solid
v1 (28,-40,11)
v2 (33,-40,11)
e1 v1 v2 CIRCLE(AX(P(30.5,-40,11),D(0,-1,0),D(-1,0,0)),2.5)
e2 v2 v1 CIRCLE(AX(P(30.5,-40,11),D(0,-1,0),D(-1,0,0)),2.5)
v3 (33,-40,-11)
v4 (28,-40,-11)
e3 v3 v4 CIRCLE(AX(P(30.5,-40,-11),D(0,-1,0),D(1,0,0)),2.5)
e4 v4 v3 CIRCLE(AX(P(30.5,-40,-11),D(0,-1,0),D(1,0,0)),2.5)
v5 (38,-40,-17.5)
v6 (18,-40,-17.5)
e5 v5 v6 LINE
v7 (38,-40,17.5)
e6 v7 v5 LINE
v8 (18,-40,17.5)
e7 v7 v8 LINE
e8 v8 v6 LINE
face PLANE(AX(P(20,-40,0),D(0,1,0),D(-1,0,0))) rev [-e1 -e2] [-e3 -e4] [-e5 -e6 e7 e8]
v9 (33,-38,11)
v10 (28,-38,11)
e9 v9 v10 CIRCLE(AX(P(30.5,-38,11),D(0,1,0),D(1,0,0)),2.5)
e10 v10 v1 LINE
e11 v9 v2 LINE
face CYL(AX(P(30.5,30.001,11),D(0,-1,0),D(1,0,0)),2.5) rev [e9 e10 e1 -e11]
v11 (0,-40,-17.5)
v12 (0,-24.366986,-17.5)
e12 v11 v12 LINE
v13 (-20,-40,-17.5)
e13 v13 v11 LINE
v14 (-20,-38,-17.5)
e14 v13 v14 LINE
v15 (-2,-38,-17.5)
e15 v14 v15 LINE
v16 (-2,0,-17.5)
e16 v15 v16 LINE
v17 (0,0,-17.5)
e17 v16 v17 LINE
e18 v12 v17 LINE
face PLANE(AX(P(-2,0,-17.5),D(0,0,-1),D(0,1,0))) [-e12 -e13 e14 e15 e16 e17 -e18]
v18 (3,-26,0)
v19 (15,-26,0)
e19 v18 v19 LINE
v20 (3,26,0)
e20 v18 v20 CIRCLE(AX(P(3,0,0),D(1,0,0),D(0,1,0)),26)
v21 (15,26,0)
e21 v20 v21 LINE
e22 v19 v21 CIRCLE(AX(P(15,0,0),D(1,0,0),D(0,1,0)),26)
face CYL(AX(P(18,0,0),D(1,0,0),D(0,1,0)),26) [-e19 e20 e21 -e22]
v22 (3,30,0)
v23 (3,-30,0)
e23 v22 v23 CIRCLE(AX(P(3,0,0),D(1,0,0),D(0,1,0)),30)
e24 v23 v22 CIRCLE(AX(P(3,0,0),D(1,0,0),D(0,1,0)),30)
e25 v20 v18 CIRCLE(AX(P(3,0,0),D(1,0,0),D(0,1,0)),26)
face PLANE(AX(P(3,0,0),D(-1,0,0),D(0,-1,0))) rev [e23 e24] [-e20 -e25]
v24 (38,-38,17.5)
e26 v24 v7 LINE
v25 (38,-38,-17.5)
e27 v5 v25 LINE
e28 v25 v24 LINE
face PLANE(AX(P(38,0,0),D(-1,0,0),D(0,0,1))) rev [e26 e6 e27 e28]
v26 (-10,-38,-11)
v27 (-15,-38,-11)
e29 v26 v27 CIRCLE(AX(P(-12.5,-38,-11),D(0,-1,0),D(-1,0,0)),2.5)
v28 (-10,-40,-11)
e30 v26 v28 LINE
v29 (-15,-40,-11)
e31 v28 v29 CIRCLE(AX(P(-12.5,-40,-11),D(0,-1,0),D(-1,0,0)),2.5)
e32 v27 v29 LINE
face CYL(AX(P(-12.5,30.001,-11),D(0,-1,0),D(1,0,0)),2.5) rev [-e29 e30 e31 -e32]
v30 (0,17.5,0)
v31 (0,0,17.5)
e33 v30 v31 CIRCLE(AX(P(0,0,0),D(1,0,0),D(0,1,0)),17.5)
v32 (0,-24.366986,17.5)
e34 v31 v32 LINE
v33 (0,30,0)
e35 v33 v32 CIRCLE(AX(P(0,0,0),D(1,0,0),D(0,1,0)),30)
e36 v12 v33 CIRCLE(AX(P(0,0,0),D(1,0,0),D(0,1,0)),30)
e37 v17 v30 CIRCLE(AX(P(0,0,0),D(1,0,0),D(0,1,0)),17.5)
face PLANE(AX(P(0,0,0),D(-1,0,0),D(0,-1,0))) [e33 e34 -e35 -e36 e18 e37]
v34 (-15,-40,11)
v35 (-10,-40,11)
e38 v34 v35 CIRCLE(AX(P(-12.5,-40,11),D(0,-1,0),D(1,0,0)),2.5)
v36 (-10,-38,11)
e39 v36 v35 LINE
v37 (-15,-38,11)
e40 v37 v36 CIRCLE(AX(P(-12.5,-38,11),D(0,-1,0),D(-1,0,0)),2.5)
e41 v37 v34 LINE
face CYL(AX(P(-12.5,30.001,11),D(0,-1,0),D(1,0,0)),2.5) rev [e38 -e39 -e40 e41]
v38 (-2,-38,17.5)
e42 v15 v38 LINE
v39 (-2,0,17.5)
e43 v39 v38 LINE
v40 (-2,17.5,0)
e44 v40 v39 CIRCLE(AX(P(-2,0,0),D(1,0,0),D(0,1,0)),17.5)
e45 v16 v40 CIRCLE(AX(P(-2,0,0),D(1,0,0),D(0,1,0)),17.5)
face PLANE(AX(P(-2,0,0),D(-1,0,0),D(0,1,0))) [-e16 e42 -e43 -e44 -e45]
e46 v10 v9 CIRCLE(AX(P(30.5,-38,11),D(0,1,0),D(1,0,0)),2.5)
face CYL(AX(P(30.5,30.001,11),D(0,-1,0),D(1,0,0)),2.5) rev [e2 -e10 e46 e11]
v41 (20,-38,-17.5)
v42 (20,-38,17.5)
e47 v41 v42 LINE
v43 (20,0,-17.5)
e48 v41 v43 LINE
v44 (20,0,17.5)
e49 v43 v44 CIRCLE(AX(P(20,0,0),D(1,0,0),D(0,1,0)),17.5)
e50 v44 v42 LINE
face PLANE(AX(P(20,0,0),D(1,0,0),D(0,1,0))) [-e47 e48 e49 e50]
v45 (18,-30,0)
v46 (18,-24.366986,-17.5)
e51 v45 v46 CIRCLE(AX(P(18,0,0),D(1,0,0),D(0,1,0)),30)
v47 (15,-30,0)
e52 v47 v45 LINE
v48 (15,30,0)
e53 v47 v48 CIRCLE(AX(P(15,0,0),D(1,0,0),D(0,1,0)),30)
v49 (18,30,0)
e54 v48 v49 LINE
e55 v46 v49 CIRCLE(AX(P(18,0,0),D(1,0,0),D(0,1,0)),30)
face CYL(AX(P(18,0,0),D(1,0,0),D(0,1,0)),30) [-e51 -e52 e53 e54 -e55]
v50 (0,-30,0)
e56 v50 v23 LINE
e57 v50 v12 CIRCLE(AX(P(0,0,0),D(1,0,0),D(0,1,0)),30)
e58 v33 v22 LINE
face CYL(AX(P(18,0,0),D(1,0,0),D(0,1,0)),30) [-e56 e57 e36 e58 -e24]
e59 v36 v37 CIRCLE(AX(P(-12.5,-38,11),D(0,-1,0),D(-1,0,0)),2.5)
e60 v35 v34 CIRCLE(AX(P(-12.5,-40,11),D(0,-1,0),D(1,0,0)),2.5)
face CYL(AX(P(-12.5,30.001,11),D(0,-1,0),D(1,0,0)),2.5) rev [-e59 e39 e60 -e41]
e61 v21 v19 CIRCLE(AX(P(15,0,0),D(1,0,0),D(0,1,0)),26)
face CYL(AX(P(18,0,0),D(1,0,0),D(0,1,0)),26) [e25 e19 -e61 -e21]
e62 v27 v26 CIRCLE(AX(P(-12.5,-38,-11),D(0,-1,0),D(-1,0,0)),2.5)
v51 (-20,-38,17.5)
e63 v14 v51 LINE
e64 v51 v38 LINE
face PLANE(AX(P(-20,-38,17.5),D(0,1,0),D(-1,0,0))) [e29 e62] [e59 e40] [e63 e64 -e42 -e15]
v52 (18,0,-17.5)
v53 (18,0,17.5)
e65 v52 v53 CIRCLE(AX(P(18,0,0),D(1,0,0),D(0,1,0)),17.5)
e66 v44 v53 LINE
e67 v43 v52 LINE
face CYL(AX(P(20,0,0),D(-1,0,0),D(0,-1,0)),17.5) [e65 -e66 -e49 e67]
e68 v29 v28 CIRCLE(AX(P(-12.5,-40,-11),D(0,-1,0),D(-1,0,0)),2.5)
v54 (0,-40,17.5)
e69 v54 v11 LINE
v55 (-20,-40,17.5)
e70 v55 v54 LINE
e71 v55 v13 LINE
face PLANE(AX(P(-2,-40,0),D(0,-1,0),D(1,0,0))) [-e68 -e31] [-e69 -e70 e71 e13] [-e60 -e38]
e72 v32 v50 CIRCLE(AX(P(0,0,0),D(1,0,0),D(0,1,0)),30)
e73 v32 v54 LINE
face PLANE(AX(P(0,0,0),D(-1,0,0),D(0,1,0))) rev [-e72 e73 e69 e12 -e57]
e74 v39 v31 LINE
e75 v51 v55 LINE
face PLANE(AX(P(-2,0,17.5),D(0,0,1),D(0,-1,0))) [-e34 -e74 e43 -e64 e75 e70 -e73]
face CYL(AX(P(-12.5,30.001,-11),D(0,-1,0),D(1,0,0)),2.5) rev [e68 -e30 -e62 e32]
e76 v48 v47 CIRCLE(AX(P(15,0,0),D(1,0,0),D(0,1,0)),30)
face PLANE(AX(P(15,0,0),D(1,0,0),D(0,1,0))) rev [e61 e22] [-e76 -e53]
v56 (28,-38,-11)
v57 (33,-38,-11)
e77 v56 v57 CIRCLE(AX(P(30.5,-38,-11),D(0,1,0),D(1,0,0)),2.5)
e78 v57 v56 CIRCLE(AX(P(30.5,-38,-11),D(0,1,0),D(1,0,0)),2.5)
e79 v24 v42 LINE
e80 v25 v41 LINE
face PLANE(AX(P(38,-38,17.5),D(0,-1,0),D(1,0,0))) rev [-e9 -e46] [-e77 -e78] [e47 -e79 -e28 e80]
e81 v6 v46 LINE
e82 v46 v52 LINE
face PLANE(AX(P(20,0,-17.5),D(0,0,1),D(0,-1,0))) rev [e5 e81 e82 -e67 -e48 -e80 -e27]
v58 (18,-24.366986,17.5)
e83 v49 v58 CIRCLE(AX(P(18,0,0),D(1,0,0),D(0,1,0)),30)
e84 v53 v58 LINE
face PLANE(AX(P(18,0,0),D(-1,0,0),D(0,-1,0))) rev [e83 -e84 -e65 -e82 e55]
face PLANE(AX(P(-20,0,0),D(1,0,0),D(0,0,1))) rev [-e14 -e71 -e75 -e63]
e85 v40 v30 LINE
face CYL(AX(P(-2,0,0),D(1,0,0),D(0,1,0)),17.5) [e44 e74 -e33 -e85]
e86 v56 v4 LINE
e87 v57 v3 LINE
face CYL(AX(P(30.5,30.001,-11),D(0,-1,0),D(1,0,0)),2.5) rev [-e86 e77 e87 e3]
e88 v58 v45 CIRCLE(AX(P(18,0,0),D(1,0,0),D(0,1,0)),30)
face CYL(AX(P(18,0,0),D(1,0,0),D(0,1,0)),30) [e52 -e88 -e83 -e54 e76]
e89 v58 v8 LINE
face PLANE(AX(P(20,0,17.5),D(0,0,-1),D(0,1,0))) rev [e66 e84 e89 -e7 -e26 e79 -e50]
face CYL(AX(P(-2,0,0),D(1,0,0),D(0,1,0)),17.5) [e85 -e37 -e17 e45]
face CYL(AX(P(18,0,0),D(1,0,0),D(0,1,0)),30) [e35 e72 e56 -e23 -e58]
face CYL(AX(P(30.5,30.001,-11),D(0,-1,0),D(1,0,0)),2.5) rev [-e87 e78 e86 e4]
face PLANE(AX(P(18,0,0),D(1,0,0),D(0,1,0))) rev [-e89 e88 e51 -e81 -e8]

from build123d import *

# Parameters (mm, degrees)
EXTRUDE_1_DEPTH     = 2
SKETCH_3_W          = 35
SKETCH_3_H          = 2
EXTRUDE_2_DEPTH     = 18
CUT_EXTRUDE_1_REACH = 87.112
SKETCH_4_R          = 2.5


with BuildPart() as part:
    # 草图1 → 旋转1 (revolve)
    with BuildSketch(Plane.XY):
        Polygon((0, 30), (0, 18.550632587), (0, 0), (18, 0), (18, 30), (15, 30), (15, 26), (3, 26), (3, 30), align=None)
    revolve(axis=Axis((18, 0, 0), (-1, 0, 0)))

    # 草图2 → 凸台-拉伸1 (add)
    with BuildSketch(Plane(origin=(18, 0, 0), x_dir=(0, 0, -1), z_dir=(1, 0, 0))):
        with BuildLine():
            Line((17.5, -40), (17.5, 0))
            ThreePointArc((17.5, 0), (0, 17.5), (-17.5, 0))
            Line((-17.5, 0), (-17.5, -40))
            Line((-17.5, -40), (17.5, -40))
        make_face()
    extrude_1 = extrude(amount=EXTRUDE_1_DEPTH)

    # 草图3 → 凸台-拉伸2 (add)
    with BuildSketch(Plane(origin=(20, 0, 0), x_dir=(0, 0, -1), z_dir=(1, 0, 0))):
        with Locations((0, -39)):
            Rectangle(SKETCH_3_W, SKETCH_3_H)
    extrude_2 = extrude(amount=EXTRUDE_2_DEPTH)

    # 镜向1: 凸台-拉伸1, 凸台-拉伸2 across plane
    add(extrude_1.mirror(Plane(origin=(9, 0, 0), x_dir=(0, 0, 1), z_dir=(1, 0, 0))))
    add(extrude_2.mirror(Plane(origin=(9, 0, 0), x_dir=(0, 0, 1), z_dir=(1, 0, 0))))

    # 草图4 → 切除-拉伸1 (cut, up to next)
    with BuildSketch(Plane.XZ.offset(40), mode=Mode.PRIVATE) as cut_extrude_1_sk1:
        with Locations((-12.5, 11)):
            Circle(SKETCH_4_R)
    cut_extrude_1_tool1 = extrude(cut_extrude_1_sk1.sketch, amount=-CUT_EXTRUDE_1_REACH, mode=Mode.PRIVATE) & part.part
    # 草图4 → 切除-拉伸1 (cut, up to next)
    with BuildSketch(Plane.XZ.offset(40), mode=Mode.PRIVATE) as cut_extrude_1_sk2:
        with Locations(Location((-12.5, -11, 0), (0, 0, 180))):
            Circle(SKETCH_4_R)
    cut_extrude_1_tool2 = extrude(cut_extrude_1_sk2.sketch, amount=-CUT_EXTRUDE_1_REACH, mode=Mode.PRIVATE) & part.part
    # 草图4 → 切除-拉伸1 (cut, up to next)
    with BuildSketch(Plane.XZ.offset(40), mode=Mode.PRIVATE) as cut_extrude_1_sk3:
        with Locations((30.5, -11)):
            Circle(SKETCH_4_R)
    cut_extrude_1_tool3 = extrude(cut_extrude_1_sk3.sketch, amount=-CUT_EXTRUDE_1_REACH, mode=Mode.PRIVATE) & part.part
    # 草图4 → 切除-拉伸1 (cut, up to next)
    with BuildSketch(Plane.XZ.offset(40), mode=Mode.PRIVATE) as cut_extrude_1_sk4:
        with Locations((30.5, 11)):
            Circle(SKETCH_4_R)
    cut_extrude_1_tool4 = extrude(cut_extrude_1_sk4.sketch, amount=-CUT_EXTRUDE_1_REACH, mode=Mode.PRIVATE) & part.part
    add(cut_extrude_1_tool1.solids().sort_by_distance((-12.5, -40, 11))[0], mode=Mode.SUBTRACT)
    add(cut_extrude_1_tool2.solids().sort_by_distance((-12.5, -40, -11))[0], mode=Mode.SUBTRACT)
    add(cut_extrude_1_tool3.solids().sort_by_distance((30.5, -40, -11))[0], mode=Mode.SUBTRACT)
    add(cut_extrude_1_tool4.solids().sort_by_distance((30.5, -40, 11))[0], mode=Mode.SUBTRACT)


solid = part.part
